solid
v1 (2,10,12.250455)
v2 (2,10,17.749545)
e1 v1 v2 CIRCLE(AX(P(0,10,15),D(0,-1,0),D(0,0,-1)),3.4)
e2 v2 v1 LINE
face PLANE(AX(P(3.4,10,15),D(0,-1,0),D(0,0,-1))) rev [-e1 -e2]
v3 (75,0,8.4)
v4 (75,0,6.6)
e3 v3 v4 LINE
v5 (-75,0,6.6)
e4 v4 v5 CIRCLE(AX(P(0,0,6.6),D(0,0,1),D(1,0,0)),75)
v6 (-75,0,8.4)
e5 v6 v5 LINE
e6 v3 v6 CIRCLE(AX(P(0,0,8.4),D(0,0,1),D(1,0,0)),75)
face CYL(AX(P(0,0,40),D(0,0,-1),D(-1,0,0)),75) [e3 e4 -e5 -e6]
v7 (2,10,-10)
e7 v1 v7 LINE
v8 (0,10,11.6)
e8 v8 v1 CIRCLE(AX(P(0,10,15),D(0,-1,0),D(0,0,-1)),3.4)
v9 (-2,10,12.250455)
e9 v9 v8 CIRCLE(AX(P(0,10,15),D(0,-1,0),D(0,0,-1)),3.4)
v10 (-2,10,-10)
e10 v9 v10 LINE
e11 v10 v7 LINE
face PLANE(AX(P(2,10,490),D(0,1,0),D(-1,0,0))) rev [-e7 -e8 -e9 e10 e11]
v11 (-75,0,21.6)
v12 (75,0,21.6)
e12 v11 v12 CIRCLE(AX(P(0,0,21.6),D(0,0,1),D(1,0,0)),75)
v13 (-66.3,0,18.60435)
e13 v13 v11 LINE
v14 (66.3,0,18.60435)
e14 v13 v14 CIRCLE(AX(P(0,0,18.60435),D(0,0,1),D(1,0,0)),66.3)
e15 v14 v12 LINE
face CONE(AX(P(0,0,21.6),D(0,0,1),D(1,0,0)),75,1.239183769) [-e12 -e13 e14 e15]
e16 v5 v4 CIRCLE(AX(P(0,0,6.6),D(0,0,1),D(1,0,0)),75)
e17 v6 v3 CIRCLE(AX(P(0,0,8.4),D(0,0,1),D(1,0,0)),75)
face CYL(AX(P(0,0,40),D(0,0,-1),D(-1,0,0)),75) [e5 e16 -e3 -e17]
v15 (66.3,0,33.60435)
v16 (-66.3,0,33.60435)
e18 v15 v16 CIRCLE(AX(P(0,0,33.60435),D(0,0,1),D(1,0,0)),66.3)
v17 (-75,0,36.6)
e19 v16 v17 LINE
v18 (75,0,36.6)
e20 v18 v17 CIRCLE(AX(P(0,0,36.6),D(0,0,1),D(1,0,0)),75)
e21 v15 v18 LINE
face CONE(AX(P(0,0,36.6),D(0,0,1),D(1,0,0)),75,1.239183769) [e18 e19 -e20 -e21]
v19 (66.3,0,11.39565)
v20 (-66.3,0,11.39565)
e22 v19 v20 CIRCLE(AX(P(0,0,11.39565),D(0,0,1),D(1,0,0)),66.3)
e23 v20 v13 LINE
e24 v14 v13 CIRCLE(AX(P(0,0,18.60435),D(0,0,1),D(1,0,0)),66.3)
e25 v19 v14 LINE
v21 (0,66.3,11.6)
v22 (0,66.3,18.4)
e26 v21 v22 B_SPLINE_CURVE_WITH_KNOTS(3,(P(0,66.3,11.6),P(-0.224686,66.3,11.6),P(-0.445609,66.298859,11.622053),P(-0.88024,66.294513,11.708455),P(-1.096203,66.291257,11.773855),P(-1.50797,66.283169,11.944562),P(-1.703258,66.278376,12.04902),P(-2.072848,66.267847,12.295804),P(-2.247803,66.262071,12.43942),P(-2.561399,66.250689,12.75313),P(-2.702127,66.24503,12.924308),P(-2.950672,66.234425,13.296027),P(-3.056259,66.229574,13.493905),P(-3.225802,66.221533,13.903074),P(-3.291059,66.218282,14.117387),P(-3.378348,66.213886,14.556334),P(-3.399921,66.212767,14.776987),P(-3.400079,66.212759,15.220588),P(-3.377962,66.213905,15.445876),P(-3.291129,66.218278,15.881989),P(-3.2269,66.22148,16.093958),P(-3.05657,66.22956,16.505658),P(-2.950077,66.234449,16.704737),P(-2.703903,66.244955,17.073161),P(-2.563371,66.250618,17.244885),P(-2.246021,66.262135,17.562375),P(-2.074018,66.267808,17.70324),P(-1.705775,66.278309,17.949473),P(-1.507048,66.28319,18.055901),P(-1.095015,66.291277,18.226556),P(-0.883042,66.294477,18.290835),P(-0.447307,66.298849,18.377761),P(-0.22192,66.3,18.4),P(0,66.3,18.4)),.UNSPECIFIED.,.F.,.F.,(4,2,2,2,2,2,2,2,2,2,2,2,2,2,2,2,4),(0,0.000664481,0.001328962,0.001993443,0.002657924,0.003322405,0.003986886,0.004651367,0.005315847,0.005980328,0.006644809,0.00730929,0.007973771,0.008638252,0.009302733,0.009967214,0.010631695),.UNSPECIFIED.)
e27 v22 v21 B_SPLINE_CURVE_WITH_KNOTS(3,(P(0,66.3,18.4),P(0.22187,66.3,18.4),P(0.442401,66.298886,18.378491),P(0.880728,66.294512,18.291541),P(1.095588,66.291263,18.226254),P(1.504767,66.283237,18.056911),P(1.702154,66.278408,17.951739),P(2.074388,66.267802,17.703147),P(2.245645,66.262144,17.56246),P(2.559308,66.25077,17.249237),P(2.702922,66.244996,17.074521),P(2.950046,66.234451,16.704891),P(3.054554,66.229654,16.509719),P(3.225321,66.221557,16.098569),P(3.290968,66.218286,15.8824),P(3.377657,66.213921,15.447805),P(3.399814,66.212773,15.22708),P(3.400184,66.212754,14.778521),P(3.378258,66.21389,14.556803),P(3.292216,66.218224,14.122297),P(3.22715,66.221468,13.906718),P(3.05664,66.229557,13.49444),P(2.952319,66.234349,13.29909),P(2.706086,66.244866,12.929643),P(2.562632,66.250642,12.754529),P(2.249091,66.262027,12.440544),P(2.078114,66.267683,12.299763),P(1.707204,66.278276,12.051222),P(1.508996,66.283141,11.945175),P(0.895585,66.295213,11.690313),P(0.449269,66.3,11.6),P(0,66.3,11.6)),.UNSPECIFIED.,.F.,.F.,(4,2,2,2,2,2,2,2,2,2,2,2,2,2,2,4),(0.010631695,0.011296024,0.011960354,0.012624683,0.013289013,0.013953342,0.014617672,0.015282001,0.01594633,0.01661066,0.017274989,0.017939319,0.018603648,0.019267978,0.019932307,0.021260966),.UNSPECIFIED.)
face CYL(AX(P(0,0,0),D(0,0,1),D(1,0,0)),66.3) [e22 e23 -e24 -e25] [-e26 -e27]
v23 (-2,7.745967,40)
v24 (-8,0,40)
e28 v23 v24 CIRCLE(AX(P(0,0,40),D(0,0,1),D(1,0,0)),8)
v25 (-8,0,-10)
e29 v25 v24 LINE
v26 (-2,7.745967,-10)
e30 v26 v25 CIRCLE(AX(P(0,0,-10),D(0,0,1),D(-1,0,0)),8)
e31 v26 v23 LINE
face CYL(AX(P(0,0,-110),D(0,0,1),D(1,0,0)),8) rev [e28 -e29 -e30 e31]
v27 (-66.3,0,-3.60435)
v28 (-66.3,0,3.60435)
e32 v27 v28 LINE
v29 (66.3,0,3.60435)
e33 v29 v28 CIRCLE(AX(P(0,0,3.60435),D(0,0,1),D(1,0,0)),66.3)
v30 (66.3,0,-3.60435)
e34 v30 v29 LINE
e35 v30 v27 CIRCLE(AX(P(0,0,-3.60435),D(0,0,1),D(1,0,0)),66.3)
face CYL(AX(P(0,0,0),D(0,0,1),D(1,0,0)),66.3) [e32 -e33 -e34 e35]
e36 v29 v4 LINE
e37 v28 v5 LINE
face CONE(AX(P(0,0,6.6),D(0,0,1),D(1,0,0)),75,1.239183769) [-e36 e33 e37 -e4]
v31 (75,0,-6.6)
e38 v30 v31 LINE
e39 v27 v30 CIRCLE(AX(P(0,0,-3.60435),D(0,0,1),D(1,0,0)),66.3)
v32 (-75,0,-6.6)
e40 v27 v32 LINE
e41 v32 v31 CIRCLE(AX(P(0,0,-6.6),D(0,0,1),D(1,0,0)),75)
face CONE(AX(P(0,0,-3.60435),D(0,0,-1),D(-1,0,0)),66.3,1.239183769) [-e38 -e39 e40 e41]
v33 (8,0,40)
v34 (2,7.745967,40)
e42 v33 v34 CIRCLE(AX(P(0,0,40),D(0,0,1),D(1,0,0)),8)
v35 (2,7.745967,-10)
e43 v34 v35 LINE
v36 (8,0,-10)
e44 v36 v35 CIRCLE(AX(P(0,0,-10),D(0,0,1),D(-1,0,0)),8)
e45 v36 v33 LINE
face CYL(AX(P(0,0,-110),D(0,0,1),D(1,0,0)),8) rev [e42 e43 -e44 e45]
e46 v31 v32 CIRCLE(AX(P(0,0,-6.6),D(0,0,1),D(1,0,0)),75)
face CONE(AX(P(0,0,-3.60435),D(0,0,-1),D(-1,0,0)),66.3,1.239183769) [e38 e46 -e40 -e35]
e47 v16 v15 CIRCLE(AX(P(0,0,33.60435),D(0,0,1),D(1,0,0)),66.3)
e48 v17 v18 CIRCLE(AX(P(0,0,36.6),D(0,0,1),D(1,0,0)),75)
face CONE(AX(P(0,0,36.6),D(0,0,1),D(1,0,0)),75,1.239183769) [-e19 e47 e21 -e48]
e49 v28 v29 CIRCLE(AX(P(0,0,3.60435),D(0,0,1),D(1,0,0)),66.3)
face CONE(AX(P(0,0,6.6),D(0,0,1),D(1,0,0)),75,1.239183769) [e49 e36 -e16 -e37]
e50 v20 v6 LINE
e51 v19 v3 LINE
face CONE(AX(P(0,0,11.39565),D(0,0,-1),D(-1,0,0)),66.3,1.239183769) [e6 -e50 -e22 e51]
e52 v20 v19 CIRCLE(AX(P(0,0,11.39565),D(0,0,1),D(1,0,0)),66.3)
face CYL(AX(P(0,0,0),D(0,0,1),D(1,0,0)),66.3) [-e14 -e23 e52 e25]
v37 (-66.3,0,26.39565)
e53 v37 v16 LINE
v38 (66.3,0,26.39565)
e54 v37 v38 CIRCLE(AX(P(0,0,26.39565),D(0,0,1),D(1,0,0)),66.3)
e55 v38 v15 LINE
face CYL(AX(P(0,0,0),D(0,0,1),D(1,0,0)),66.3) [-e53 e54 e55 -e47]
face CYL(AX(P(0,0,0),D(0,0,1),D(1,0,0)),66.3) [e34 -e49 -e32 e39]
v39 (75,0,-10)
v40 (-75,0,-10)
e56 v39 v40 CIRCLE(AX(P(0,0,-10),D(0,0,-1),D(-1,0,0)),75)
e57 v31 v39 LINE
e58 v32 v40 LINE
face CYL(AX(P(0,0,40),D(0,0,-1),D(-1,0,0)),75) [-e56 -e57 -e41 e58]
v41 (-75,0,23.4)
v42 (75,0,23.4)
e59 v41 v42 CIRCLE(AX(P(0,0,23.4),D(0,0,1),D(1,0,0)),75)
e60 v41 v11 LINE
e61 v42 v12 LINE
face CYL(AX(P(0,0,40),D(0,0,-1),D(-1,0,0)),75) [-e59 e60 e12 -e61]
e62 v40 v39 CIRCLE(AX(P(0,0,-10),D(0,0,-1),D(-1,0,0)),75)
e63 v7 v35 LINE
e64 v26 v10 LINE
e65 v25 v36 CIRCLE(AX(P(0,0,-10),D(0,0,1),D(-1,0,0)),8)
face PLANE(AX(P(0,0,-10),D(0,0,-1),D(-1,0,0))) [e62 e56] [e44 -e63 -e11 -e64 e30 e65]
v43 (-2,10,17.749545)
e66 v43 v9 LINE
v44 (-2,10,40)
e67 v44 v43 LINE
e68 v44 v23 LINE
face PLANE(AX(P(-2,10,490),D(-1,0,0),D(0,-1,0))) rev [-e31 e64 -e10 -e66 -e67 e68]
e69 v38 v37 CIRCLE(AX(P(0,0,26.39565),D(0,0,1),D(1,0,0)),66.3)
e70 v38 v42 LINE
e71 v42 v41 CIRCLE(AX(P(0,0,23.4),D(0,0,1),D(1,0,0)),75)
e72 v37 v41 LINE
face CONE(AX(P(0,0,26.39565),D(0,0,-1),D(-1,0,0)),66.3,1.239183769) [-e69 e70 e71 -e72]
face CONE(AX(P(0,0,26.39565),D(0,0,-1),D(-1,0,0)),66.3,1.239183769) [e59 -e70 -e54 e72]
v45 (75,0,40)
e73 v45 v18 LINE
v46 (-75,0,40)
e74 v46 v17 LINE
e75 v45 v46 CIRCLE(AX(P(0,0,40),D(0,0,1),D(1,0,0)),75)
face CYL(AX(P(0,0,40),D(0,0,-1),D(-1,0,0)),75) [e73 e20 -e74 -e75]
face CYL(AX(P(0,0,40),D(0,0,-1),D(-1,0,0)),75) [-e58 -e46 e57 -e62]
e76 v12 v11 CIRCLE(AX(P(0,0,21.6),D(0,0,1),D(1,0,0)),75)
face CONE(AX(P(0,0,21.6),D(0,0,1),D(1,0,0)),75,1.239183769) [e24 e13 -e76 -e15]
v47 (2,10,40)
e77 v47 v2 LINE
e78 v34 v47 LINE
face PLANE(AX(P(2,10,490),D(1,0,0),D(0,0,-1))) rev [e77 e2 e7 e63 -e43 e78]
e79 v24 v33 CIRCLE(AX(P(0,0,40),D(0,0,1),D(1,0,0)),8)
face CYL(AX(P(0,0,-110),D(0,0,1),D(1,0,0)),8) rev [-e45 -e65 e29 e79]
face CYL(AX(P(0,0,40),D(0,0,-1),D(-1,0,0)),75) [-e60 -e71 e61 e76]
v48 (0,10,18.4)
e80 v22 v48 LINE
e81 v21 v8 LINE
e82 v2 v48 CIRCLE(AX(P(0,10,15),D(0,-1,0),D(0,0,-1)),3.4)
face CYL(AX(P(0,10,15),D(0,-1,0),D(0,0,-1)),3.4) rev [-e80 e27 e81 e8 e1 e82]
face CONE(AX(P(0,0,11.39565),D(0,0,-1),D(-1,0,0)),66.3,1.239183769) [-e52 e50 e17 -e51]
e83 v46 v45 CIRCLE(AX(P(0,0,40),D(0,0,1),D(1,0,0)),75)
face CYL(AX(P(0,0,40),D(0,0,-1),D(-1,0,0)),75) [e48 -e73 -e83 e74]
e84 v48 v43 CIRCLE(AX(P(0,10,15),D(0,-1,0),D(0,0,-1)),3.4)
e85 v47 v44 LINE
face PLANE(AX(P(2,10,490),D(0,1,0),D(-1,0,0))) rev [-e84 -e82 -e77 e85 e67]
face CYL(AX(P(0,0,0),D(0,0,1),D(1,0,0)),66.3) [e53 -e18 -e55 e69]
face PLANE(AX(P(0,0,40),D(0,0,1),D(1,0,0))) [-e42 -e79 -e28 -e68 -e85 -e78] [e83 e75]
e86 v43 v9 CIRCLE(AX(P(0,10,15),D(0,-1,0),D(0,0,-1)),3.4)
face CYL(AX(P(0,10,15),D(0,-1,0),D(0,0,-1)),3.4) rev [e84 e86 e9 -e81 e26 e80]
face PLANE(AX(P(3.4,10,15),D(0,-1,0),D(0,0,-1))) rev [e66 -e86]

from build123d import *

# Parameters (mm, degrees)
SKETCH1_R           = 75
BOSS_EXTRUDE1_DEPTH = 40
SKETCH2_R           = 8
CUT_EXTRUDE1_DEPTH  = 150
SKETCH10_R          = 100
CUT_EXTRUDE5_DEPTH  = 20
SKETCH11_R          = 30
SKETCH11_R_2        = 8
BOSS_EXTRUDE2_DEPTH = 20
SKETCH12_R          = 130
CUT_EXTRUDE6_DEPTH  = 30
SKETCH13_W          = 4
SKETCH13_H          = 4
CUT_EXTRUDE7_DEPTH  = 500
SKETCH15_W          = 3.4
SKETCH15_H          = 65


with BuildPart() as part:
    # Sketch1 → Boss-Extrude1 (new, symmetric)
    with BuildSketch(Plane.XY):
        Circle(SKETCH1_R)
    extrude(amount=BOSS_EXTRUDE1_DEPTH, both=True)

    # Sketch2 → Cut-Extrude1 (cut)
    with BuildSketch(Plane.XY.offset(40)):
        Circle(SKETCH2_R)
    extrude(amount=-CUT_EXTRUDE1_DEPTH, mode=Mode.SUBTRACT)

    # Sketch4 → Cut-Revolve1 (revolve, cut)
    with BuildSketch(Plane(origin=(0, 0, 0), x_dir=(0, 0, -1), z_dir=(1, 0, 0)), mode=Mode.PRIVATE) as cut_revolve1_sk:
        Polygon((-40, 75), (-36.6, 75), (-33.604349764, 66.3), (-26.395650236, 66.3), (-23.4, 75), (-21.6, 75), (-18.604349764, 66.3), (-11.395650236, 66.3), (-8.4, 75), (-6.6, 75), (-3.604349764, 66.3), (3.604349764, 66.3), (6.6, 75), (10, 75), (10, 161.050459045), (-40, 161.050459045), align=None)
    revolve(cut_revolve1_sk.sketch.rotate(Axis((0, 0, 0), (0, 0, -1)), 90), axis=Axis((0, 0, 0), (0, 0, -1)), mode=Mode.SUBTRACT)

    # Sketch10 → Cut-Extrude5 (cut)
    with BuildSketch(Plane(origin=(0, 0, -40), x_dir=(-1, 0, 0), z_dir=(0, 0, -1))):
        Circle(SKETCH10_R)
    extrude(amount=-CUT_EXTRUDE5_DEPTH, mode=Mode.SUBTRACT)

    # Sketch11 → Boss-Extrude2 (add)
    with BuildSketch(Plane(origin=(0, 0, -20), x_dir=(-1, 0, 0), z_dir=(0, 0, -1))):
        Circle(SKETCH11_R)
        with Locations(Location((0, 0, 0), (0, 0, 180))):
            Circle(SKETCH11_R_2, mode=Mode.SUBTRACT)
    extrude(amount=BOSS_EXTRUDE2_DEPTH)

    # Sketch12 → Cut-Extrude6 (cut)
    with BuildSketch(Plane(origin=(0, 0, -40), x_dir=(-1, 0, 0), z_dir=(0, 0, -1))):
        Circle(SKETCH12_R)
    extrude(amount=-CUT_EXTRUDE6_DEPTH, mode=Mode.SUBTRACT)

    # Sketch13 → Cut-Extrude7 (cut)
    with BuildSketch(Plane(origin=(0, 0, -10), x_dir=(-1, 0, 0), z_dir=(0, 0, -1))):
        with Locations((0, 8)):
            Rectangle(SKETCH13_W, SKETCH13_H)
    extrude(amount=-CUT_EXTRUDE7_DEPTH, mode=Mode.SUBTRACT)

    # Sketch15 → M8 Tapped Hole1 (revolve, cut)
    with BuildSketch(Plane(origin=(0, 10, 15), x_dir=(0, 0, -1), z_dir=(1, 0, 0))):
        with Locations((1.7, 32.5)):
            Rectangle(SKETCH15_W, SKETCH15_H)
    revolve(axis=Axis((0, 3.65, 15), (0, 1, 0)), mode=Mode.SUBTRACT)


solid = part.part
